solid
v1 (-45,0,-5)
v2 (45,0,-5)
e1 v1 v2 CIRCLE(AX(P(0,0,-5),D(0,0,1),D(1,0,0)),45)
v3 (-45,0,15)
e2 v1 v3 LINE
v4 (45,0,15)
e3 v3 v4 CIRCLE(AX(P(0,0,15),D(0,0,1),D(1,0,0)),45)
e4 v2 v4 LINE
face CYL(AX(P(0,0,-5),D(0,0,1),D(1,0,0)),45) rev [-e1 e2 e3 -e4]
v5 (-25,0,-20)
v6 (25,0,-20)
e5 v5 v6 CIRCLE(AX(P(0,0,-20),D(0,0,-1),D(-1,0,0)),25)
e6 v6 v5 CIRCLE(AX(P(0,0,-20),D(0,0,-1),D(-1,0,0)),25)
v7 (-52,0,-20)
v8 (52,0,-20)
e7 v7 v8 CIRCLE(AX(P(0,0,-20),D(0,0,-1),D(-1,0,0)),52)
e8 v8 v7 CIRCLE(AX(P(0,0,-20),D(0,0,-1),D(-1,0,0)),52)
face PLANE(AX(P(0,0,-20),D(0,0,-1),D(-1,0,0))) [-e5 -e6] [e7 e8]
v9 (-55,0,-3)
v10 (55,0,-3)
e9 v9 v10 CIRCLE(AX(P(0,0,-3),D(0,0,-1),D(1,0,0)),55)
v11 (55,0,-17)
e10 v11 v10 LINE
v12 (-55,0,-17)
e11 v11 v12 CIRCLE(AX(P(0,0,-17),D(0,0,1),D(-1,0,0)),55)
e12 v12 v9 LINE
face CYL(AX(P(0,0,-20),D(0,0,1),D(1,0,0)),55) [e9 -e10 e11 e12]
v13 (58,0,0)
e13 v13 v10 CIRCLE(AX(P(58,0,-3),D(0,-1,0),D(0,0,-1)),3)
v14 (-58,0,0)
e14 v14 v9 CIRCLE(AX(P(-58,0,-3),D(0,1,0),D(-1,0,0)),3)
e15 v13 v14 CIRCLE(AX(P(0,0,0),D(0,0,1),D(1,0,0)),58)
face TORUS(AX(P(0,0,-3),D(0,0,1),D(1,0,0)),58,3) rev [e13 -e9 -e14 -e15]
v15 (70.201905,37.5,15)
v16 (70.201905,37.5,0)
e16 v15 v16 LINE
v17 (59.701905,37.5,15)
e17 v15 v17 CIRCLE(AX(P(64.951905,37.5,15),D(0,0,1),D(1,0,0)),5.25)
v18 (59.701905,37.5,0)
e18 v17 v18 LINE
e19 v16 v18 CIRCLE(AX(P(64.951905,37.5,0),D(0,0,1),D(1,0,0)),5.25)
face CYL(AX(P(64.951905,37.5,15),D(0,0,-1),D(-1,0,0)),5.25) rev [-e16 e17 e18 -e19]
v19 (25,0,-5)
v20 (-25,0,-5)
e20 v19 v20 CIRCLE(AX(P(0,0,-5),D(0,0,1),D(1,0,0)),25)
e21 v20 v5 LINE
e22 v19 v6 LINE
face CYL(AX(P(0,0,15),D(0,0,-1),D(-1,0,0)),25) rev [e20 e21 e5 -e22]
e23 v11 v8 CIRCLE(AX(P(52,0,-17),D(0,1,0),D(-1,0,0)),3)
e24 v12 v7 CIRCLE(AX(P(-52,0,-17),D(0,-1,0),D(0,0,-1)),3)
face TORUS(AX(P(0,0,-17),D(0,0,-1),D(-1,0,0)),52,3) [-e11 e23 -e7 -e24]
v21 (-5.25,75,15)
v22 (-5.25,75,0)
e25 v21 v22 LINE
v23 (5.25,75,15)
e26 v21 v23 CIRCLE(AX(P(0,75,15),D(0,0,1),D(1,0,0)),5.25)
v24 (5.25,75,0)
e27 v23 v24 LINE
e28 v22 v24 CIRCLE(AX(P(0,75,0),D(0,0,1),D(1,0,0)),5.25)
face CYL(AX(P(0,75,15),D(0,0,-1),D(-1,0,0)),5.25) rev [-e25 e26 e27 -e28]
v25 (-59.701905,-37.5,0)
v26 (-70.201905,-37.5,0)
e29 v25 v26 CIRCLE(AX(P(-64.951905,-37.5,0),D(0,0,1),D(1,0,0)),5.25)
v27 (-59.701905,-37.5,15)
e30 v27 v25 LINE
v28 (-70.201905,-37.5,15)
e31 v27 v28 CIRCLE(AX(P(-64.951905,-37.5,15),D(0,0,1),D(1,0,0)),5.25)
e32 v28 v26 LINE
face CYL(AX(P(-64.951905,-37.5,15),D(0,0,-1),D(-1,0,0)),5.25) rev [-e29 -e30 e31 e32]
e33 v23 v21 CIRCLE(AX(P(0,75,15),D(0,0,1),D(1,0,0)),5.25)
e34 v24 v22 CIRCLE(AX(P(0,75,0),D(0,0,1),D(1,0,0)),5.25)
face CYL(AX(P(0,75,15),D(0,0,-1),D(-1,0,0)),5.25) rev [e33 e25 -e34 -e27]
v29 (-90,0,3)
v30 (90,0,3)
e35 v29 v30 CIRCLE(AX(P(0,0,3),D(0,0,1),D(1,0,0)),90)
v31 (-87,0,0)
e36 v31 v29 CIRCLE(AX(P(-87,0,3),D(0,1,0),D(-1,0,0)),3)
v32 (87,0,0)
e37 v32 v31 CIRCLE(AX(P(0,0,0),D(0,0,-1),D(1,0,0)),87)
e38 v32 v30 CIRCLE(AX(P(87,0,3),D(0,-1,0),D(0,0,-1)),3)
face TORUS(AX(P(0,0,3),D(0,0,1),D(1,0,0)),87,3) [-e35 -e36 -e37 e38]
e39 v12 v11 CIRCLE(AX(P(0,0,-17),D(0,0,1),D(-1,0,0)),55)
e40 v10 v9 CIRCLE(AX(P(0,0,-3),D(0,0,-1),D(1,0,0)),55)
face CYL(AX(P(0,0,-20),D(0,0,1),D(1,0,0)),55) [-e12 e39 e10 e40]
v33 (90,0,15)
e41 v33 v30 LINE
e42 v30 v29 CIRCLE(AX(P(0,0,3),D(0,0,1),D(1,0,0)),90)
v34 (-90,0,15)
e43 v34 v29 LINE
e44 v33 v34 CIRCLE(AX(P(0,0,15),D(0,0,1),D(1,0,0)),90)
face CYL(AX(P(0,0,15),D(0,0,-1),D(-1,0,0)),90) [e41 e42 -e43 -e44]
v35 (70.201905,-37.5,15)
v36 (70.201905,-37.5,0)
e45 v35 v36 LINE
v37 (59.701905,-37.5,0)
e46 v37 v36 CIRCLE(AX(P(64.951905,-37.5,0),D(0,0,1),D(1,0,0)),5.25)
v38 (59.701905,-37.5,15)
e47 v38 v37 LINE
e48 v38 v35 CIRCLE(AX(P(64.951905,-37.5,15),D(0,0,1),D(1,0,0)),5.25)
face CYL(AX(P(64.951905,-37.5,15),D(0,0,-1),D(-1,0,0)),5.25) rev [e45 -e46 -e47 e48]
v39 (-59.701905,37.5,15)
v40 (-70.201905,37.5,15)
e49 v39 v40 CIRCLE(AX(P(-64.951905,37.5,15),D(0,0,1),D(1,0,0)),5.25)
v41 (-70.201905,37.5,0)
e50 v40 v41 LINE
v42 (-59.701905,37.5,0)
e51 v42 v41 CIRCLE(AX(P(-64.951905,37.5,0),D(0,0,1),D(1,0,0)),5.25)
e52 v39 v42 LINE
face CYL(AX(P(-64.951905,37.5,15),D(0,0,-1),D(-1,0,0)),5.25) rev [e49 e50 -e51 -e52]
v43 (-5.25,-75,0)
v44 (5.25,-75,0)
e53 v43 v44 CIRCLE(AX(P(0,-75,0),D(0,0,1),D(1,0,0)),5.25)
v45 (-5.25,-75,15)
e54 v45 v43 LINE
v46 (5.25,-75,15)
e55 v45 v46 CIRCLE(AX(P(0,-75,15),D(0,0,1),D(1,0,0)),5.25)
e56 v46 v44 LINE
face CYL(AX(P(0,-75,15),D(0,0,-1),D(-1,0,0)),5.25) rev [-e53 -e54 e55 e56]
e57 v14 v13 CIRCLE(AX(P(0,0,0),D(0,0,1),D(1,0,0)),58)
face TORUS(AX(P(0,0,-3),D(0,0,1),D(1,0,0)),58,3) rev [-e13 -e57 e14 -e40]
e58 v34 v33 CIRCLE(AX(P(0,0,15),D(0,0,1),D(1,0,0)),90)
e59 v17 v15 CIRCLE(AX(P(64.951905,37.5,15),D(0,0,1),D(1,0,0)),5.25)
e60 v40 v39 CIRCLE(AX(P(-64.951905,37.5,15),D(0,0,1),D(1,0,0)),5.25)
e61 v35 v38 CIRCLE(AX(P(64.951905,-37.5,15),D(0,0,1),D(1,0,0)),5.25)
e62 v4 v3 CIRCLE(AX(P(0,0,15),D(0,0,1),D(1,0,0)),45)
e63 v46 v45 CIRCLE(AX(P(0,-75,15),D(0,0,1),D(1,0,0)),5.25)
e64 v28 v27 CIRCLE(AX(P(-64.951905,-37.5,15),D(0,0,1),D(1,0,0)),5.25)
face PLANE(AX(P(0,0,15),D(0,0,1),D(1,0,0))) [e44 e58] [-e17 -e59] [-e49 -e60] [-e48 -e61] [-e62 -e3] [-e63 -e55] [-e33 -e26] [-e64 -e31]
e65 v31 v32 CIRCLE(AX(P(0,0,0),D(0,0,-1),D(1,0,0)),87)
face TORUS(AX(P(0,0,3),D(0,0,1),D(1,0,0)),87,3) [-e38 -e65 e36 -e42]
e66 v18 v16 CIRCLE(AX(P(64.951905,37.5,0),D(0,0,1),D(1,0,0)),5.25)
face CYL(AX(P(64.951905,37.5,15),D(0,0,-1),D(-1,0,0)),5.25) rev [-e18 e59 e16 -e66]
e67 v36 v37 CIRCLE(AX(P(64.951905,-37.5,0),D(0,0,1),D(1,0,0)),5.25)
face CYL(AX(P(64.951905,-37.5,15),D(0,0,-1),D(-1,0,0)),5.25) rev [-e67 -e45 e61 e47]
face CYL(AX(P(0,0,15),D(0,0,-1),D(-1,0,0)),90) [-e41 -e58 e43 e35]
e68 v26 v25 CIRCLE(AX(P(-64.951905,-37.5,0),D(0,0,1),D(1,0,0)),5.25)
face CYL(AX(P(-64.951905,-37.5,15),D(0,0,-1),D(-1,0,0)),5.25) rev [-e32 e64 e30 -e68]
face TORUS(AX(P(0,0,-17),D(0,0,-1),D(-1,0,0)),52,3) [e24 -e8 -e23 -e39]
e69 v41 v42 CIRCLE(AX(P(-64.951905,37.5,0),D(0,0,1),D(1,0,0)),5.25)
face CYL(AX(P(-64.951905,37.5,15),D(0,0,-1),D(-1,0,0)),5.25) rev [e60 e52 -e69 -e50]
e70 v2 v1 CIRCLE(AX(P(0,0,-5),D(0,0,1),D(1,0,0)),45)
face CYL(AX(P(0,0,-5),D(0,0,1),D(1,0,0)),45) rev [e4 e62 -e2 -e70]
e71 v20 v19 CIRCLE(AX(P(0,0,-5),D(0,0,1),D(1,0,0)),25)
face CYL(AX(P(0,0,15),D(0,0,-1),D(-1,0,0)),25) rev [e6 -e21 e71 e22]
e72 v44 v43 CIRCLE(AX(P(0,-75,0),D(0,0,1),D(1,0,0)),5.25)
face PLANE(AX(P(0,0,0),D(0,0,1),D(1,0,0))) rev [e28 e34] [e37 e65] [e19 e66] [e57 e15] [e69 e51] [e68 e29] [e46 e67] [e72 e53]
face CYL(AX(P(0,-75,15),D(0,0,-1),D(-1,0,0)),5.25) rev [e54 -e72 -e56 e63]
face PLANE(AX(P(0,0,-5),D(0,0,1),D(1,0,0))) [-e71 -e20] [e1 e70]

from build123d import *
from build123d.topology import SkipClean

# Parameters (mm, degrees)
SKETCH_1_R          = 90
SKETCH_1_R_2        = 25
SKETCH_1_R_3        = 5.25
EXTRUDE_1_DEPTH     = 15
EXTRUDE_START       = 20
SKETCH_2_R          = 55
SKETCH_2_R_2        = 25
EXTRUDE_2_DEPTH     = 20
SKETCH_3_R          = 45
CUT_EXTRUDE_1_DEPTH = 20
FILLET_1_R          = 3


with BuildPart() as part:
    # 草图1 → 凸台-拉伸1 (new body)
    with BuildSketch(Plane.XY):
        Circle(SKETCH_1_R)
        Circle(SKETCH_1_R_2, mode=Mode.SUBTRACT)
        with Locations((0, 75)):
            Circle(SKETCH_1_R_3, mode=Mode.SUBTRACT)
        with Locations((64.951905284, 37.5)):
            Circle(SKETCH_1_R_3, mode=Mode.SUBTRACT)
        with Locations((64.951905284, -37.5)):
            Circle(SKETCH_1_R_3, mode=Mode.SUBTRACT)
        with Locations((0, -75)):
            Circle(SKETCH_1_R_3, mode=Mode.SUBTRACT)
        with Locations((-64.951905284, -37.5)):
            Circle(SKETCH_1_R_3, mode=Mode.SUBTRACT)
        with Locations((-64.951905284, 37.5)):
            Circle(SKETCH_1_R_3, mode=Mode.SUBTRACT)
    extrude(amount=EXTRUDE_1_DEPTH)

    # 草图2 → 凸台-拉伸2 (add)
    with SkipClean():  # the faces are left unmerged after this step: merging them gives an invalid solid
        with BuildSketch(Plane(origin=(0, 0, 0), x_dir=(-1, 0, 0), z_dir=(0, 0, -1)).offset(EXTRUDE_START)):
            with Locations(Location((0, 0, 0), (0, 0, 180))):
                Circle(SKETCH_2_R)
            Circle(SKETCH_2_R_2, mode=Mode.SUBTRACT)
        extrude(amount=-EXTRUDE_2_DEPTH)

    # 草图3 → 切除-拉伸1 (cut)
    with BuildSketch(Plane.XY.offset(15)):
        Circle(SKETCH_3_R)
    extrude(amount=-CUT_EXTRUDE_1_DEPTH, mode=Mode.SUBTRACT)

    # 圆角1
    fillet_1_edges = [part.edges().sort_by_distance(p)[0] for p in [
        (-90, 0, 0),
        (-55, 0, 0),
        (-55, 0, -20),
    ]]
    fillet(fillet_1_edges, radius=FILLET_1_R)


solid = part.part
